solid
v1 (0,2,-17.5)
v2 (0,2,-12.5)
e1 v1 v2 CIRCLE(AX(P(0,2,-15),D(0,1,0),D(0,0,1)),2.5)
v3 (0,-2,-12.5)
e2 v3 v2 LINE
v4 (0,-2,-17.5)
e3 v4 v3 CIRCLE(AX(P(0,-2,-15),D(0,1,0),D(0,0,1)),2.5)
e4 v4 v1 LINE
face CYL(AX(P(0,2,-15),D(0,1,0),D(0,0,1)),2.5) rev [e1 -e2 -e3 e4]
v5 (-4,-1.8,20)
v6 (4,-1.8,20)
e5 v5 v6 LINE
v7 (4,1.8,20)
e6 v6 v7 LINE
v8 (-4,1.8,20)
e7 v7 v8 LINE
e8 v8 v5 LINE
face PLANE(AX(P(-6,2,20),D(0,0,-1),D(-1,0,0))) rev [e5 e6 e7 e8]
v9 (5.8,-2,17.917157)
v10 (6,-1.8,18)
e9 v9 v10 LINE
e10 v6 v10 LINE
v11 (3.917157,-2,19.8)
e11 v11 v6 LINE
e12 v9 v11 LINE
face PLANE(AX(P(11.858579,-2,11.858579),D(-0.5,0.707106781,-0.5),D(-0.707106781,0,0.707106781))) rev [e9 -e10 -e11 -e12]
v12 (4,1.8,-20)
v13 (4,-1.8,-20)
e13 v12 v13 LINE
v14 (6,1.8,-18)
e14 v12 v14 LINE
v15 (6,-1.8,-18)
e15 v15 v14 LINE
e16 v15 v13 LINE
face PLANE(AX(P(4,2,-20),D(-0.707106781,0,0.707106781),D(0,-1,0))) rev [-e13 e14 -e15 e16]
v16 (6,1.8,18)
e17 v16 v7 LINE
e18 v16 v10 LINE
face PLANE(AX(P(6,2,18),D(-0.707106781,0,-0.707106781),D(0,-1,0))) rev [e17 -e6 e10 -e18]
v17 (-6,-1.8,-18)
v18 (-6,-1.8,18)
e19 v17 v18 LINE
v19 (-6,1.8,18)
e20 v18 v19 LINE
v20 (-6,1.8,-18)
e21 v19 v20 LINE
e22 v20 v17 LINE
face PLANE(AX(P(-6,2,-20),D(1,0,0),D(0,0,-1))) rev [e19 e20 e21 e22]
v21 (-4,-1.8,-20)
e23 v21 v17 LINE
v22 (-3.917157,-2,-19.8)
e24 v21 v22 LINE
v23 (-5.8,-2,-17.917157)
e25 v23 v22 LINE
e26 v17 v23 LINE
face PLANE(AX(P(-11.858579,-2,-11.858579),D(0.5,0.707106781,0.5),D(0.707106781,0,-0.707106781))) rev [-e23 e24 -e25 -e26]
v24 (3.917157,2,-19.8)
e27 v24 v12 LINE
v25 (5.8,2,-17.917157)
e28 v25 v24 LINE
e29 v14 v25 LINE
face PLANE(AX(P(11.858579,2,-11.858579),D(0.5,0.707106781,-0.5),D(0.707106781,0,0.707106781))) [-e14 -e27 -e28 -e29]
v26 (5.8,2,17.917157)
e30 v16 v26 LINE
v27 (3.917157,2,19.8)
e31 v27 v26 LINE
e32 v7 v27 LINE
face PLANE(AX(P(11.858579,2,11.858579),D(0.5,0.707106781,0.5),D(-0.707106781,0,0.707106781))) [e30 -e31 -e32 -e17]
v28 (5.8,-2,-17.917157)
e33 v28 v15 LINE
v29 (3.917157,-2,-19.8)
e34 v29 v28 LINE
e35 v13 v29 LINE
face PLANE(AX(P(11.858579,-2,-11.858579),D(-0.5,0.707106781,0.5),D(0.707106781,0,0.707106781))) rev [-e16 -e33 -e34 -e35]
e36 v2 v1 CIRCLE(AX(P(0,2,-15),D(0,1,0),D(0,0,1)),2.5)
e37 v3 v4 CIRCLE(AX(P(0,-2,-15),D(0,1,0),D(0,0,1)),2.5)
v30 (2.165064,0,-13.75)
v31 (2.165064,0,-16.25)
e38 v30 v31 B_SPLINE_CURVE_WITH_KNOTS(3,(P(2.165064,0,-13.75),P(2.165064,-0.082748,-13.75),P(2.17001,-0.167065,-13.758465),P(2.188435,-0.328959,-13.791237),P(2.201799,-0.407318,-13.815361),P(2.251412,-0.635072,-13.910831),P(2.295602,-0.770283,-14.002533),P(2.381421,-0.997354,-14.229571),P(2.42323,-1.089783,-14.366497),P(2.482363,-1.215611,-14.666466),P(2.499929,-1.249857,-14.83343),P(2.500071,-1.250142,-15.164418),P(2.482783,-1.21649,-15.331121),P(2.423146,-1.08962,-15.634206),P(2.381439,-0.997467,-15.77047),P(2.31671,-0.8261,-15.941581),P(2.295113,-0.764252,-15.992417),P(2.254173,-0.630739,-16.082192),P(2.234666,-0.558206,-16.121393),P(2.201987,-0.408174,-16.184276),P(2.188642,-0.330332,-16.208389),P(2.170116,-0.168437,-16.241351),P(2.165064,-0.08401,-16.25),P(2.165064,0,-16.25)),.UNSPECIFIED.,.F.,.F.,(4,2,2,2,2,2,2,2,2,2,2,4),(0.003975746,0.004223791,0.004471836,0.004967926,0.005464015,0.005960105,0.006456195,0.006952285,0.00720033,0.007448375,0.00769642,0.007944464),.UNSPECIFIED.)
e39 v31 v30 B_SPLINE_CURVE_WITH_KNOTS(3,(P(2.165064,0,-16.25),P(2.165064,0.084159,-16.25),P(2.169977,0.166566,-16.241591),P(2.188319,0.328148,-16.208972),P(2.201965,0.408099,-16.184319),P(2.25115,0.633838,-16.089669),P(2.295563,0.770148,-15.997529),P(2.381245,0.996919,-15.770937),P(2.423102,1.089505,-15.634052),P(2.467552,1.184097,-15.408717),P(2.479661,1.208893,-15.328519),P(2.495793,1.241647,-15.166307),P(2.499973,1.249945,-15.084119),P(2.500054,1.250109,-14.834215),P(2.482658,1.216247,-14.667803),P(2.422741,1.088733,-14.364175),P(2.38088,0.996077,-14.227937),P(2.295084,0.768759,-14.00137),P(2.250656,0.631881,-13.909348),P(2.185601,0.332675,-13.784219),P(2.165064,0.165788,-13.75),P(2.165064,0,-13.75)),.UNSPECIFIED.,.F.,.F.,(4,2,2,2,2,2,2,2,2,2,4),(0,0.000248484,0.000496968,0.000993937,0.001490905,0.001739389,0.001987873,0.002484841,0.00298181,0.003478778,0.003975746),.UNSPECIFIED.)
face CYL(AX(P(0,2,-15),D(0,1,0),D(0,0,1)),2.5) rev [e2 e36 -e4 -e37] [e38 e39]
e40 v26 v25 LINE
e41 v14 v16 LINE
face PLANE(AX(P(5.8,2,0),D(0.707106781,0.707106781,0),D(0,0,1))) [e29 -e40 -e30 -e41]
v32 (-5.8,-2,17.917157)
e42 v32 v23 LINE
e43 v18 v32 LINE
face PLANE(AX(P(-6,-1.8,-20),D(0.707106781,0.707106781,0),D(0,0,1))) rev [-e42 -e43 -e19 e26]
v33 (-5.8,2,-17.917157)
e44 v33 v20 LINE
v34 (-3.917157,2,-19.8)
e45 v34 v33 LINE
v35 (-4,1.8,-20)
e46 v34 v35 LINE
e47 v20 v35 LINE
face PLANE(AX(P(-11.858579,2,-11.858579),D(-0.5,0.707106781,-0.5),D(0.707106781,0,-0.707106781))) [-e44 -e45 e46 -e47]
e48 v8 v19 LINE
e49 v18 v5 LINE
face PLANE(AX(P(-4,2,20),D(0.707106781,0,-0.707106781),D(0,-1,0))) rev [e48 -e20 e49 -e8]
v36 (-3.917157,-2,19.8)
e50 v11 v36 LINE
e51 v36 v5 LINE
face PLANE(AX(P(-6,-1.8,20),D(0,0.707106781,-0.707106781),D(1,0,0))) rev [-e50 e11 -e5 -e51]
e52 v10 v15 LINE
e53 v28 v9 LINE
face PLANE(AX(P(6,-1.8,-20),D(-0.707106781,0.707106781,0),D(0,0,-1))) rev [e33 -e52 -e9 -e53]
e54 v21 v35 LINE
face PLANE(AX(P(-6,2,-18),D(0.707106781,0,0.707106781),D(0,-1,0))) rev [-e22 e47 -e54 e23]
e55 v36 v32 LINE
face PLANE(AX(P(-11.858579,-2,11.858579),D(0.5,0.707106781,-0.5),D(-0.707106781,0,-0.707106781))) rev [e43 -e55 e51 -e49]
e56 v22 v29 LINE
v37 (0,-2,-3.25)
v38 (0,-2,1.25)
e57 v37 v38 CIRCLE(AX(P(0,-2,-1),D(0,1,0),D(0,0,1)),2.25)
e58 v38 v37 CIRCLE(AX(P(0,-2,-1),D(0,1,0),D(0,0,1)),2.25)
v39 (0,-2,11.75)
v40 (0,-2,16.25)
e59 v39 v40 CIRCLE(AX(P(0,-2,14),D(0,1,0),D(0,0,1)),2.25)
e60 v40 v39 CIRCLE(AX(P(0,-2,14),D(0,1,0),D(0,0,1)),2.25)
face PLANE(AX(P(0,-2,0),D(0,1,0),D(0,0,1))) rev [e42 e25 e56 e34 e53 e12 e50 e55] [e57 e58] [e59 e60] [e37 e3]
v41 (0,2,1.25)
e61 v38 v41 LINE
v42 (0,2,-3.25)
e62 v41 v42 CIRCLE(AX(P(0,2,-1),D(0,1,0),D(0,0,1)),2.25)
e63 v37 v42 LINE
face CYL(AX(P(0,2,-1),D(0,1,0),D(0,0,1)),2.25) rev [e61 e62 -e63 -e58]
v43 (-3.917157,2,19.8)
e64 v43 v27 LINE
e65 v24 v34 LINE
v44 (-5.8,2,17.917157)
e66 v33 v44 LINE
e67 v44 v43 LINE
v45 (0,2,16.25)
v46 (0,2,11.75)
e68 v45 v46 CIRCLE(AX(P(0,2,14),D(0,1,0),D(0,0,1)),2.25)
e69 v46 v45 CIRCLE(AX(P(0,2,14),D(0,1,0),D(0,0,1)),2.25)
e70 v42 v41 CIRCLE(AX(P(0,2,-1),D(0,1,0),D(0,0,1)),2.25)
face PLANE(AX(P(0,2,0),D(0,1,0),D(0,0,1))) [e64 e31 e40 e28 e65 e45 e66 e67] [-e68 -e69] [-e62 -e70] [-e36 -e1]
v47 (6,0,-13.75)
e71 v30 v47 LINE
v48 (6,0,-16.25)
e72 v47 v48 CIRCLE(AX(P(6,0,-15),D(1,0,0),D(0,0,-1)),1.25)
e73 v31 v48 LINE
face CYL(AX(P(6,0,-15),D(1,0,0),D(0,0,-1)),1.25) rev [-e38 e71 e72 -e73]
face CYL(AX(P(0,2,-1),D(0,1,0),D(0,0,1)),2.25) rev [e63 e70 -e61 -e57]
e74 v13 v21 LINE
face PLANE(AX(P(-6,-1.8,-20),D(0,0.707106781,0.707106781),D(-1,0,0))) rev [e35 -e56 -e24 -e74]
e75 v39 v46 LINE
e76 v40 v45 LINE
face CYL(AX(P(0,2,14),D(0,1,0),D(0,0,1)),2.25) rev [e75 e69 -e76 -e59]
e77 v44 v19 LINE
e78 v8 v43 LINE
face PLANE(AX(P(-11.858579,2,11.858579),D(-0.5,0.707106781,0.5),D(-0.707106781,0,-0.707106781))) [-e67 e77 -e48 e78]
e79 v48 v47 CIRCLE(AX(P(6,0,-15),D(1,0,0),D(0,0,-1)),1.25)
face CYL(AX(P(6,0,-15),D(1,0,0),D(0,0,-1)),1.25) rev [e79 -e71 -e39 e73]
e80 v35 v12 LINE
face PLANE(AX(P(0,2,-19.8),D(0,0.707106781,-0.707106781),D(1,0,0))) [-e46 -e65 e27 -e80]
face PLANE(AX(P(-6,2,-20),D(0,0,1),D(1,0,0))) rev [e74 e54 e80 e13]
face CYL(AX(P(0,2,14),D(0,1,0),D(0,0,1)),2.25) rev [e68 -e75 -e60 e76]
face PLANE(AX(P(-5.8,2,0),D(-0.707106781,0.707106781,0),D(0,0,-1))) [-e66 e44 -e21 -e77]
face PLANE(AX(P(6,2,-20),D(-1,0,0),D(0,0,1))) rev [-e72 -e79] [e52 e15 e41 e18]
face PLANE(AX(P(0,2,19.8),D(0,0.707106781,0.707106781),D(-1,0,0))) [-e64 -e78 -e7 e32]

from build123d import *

# Parameters (mm, degrees)
SKETCH1_W                  = 12
SKETCH1_H                  = 40
BOSS_EXTRUDE1_DEPTH        = 2
CHAMFER1_SIZE              = 2
M6_TAPPED_HOLE1_D          = 5
F_4_5_4_5_DIAMETER_HOLE1_D = 4.5
M3_TAPPED_HOLE1_REACH      = 25.409
M3_TAPPED_HOLE1_BORE_R     = 1.25
CHAMFER2_SIZE              = 0.2


with BuildPart() as part:
    # Sketch1 → Boss-Extrude1 (new, symmetric)
    with BuildSketch(Plane(origin=(0, 0, 0), x_dir=(1, 0, 0), z_dir=(0, 1, 0))):
        Rectangle(SKETCH1_W, SKETCH1_H)
    extrude(amount=BOSS_EXTRUDE1_DEPTH, both=True)

    # Chamfer1
    chamfer1_edges = [part.edges().sort_by_distance(p)[0] for p in [
        (6, 0, 20),
        (-6, 0, 20),
        (-6, 0, -20),
        (6, 0, -20),
    ]]
    chamfer(chamfer1_edges, length=CHAMFER1_SIZE)

    # M6 Tapped Hole1 (through all)
    with Locations(Plane(origin=(0, 2, 0), x_dir=(1, 0, 0), z_dir=(0, 1, 0))):
        with Locations((0, 15)):
            Hole(M6_TAPPED_HOLE1_D / 2)

    # Ø4.5 (4.5) Diameter Hole1 (through all)
    with Locations(Plane(origin=(0, 2, 0), x_dir=(1, 0, 0), z_dir=(0, 1, 0))):
        with Locations((0, 1), (0, -14)):
            Hole(F_4_5_4_5_DIAMETER_HOLE1_D / 2)

    # M3 Tapped Hole1 bore → M3 Tapped Hole1 (cut, up to next)
    with BuildSketch(Plane(origin=(6, 0, 0), x_dir=(0, 0, -1), z_dir=(1, 0, 0)), mode=Mode.PRIVATE) as m3_tapped_hole1_sk1:
        with Locations((15, 0)):
            Circle(M3_TAPPED_HOLE1_BORE_R)
    m3_tapped_hole1_tool1 = extrude(m3_tapped_hole1_sk1.sketch, amount=-M3_TAPPED_HOLE1_REACH, mode=Mode.PRIVATE) & part.part
    add(m3_tapped_hole1_tool1.solids().sort_by_distance((6, 0, -15))[0], mode=Mode.SUBTRACT)

    # Chamfer2
    chamfer2_edges = [part.edges().sort_by_distance(p)[0] for p in [
        (-6, -2, 0),
        (-6, 2, 0),
        (6, -2, 0),
        (0, -2, 20),
        (0, -2, -20),
        (-5, -2, 19),
        (5, -2, 19),
        (5, -2, -19),
        (-5, -2, -19),
        (0, 2, -20),
        (6, 2, 0),
        (0, 2, 20),
        (-5, 2, 19),
        (5, 2, 19),
        (5, 2, -19),
        (-5, 2, -19),
    ]]
    chamfer(chamfer2_edges, length=CHAMFER2_SIZE)


solid = part.part
